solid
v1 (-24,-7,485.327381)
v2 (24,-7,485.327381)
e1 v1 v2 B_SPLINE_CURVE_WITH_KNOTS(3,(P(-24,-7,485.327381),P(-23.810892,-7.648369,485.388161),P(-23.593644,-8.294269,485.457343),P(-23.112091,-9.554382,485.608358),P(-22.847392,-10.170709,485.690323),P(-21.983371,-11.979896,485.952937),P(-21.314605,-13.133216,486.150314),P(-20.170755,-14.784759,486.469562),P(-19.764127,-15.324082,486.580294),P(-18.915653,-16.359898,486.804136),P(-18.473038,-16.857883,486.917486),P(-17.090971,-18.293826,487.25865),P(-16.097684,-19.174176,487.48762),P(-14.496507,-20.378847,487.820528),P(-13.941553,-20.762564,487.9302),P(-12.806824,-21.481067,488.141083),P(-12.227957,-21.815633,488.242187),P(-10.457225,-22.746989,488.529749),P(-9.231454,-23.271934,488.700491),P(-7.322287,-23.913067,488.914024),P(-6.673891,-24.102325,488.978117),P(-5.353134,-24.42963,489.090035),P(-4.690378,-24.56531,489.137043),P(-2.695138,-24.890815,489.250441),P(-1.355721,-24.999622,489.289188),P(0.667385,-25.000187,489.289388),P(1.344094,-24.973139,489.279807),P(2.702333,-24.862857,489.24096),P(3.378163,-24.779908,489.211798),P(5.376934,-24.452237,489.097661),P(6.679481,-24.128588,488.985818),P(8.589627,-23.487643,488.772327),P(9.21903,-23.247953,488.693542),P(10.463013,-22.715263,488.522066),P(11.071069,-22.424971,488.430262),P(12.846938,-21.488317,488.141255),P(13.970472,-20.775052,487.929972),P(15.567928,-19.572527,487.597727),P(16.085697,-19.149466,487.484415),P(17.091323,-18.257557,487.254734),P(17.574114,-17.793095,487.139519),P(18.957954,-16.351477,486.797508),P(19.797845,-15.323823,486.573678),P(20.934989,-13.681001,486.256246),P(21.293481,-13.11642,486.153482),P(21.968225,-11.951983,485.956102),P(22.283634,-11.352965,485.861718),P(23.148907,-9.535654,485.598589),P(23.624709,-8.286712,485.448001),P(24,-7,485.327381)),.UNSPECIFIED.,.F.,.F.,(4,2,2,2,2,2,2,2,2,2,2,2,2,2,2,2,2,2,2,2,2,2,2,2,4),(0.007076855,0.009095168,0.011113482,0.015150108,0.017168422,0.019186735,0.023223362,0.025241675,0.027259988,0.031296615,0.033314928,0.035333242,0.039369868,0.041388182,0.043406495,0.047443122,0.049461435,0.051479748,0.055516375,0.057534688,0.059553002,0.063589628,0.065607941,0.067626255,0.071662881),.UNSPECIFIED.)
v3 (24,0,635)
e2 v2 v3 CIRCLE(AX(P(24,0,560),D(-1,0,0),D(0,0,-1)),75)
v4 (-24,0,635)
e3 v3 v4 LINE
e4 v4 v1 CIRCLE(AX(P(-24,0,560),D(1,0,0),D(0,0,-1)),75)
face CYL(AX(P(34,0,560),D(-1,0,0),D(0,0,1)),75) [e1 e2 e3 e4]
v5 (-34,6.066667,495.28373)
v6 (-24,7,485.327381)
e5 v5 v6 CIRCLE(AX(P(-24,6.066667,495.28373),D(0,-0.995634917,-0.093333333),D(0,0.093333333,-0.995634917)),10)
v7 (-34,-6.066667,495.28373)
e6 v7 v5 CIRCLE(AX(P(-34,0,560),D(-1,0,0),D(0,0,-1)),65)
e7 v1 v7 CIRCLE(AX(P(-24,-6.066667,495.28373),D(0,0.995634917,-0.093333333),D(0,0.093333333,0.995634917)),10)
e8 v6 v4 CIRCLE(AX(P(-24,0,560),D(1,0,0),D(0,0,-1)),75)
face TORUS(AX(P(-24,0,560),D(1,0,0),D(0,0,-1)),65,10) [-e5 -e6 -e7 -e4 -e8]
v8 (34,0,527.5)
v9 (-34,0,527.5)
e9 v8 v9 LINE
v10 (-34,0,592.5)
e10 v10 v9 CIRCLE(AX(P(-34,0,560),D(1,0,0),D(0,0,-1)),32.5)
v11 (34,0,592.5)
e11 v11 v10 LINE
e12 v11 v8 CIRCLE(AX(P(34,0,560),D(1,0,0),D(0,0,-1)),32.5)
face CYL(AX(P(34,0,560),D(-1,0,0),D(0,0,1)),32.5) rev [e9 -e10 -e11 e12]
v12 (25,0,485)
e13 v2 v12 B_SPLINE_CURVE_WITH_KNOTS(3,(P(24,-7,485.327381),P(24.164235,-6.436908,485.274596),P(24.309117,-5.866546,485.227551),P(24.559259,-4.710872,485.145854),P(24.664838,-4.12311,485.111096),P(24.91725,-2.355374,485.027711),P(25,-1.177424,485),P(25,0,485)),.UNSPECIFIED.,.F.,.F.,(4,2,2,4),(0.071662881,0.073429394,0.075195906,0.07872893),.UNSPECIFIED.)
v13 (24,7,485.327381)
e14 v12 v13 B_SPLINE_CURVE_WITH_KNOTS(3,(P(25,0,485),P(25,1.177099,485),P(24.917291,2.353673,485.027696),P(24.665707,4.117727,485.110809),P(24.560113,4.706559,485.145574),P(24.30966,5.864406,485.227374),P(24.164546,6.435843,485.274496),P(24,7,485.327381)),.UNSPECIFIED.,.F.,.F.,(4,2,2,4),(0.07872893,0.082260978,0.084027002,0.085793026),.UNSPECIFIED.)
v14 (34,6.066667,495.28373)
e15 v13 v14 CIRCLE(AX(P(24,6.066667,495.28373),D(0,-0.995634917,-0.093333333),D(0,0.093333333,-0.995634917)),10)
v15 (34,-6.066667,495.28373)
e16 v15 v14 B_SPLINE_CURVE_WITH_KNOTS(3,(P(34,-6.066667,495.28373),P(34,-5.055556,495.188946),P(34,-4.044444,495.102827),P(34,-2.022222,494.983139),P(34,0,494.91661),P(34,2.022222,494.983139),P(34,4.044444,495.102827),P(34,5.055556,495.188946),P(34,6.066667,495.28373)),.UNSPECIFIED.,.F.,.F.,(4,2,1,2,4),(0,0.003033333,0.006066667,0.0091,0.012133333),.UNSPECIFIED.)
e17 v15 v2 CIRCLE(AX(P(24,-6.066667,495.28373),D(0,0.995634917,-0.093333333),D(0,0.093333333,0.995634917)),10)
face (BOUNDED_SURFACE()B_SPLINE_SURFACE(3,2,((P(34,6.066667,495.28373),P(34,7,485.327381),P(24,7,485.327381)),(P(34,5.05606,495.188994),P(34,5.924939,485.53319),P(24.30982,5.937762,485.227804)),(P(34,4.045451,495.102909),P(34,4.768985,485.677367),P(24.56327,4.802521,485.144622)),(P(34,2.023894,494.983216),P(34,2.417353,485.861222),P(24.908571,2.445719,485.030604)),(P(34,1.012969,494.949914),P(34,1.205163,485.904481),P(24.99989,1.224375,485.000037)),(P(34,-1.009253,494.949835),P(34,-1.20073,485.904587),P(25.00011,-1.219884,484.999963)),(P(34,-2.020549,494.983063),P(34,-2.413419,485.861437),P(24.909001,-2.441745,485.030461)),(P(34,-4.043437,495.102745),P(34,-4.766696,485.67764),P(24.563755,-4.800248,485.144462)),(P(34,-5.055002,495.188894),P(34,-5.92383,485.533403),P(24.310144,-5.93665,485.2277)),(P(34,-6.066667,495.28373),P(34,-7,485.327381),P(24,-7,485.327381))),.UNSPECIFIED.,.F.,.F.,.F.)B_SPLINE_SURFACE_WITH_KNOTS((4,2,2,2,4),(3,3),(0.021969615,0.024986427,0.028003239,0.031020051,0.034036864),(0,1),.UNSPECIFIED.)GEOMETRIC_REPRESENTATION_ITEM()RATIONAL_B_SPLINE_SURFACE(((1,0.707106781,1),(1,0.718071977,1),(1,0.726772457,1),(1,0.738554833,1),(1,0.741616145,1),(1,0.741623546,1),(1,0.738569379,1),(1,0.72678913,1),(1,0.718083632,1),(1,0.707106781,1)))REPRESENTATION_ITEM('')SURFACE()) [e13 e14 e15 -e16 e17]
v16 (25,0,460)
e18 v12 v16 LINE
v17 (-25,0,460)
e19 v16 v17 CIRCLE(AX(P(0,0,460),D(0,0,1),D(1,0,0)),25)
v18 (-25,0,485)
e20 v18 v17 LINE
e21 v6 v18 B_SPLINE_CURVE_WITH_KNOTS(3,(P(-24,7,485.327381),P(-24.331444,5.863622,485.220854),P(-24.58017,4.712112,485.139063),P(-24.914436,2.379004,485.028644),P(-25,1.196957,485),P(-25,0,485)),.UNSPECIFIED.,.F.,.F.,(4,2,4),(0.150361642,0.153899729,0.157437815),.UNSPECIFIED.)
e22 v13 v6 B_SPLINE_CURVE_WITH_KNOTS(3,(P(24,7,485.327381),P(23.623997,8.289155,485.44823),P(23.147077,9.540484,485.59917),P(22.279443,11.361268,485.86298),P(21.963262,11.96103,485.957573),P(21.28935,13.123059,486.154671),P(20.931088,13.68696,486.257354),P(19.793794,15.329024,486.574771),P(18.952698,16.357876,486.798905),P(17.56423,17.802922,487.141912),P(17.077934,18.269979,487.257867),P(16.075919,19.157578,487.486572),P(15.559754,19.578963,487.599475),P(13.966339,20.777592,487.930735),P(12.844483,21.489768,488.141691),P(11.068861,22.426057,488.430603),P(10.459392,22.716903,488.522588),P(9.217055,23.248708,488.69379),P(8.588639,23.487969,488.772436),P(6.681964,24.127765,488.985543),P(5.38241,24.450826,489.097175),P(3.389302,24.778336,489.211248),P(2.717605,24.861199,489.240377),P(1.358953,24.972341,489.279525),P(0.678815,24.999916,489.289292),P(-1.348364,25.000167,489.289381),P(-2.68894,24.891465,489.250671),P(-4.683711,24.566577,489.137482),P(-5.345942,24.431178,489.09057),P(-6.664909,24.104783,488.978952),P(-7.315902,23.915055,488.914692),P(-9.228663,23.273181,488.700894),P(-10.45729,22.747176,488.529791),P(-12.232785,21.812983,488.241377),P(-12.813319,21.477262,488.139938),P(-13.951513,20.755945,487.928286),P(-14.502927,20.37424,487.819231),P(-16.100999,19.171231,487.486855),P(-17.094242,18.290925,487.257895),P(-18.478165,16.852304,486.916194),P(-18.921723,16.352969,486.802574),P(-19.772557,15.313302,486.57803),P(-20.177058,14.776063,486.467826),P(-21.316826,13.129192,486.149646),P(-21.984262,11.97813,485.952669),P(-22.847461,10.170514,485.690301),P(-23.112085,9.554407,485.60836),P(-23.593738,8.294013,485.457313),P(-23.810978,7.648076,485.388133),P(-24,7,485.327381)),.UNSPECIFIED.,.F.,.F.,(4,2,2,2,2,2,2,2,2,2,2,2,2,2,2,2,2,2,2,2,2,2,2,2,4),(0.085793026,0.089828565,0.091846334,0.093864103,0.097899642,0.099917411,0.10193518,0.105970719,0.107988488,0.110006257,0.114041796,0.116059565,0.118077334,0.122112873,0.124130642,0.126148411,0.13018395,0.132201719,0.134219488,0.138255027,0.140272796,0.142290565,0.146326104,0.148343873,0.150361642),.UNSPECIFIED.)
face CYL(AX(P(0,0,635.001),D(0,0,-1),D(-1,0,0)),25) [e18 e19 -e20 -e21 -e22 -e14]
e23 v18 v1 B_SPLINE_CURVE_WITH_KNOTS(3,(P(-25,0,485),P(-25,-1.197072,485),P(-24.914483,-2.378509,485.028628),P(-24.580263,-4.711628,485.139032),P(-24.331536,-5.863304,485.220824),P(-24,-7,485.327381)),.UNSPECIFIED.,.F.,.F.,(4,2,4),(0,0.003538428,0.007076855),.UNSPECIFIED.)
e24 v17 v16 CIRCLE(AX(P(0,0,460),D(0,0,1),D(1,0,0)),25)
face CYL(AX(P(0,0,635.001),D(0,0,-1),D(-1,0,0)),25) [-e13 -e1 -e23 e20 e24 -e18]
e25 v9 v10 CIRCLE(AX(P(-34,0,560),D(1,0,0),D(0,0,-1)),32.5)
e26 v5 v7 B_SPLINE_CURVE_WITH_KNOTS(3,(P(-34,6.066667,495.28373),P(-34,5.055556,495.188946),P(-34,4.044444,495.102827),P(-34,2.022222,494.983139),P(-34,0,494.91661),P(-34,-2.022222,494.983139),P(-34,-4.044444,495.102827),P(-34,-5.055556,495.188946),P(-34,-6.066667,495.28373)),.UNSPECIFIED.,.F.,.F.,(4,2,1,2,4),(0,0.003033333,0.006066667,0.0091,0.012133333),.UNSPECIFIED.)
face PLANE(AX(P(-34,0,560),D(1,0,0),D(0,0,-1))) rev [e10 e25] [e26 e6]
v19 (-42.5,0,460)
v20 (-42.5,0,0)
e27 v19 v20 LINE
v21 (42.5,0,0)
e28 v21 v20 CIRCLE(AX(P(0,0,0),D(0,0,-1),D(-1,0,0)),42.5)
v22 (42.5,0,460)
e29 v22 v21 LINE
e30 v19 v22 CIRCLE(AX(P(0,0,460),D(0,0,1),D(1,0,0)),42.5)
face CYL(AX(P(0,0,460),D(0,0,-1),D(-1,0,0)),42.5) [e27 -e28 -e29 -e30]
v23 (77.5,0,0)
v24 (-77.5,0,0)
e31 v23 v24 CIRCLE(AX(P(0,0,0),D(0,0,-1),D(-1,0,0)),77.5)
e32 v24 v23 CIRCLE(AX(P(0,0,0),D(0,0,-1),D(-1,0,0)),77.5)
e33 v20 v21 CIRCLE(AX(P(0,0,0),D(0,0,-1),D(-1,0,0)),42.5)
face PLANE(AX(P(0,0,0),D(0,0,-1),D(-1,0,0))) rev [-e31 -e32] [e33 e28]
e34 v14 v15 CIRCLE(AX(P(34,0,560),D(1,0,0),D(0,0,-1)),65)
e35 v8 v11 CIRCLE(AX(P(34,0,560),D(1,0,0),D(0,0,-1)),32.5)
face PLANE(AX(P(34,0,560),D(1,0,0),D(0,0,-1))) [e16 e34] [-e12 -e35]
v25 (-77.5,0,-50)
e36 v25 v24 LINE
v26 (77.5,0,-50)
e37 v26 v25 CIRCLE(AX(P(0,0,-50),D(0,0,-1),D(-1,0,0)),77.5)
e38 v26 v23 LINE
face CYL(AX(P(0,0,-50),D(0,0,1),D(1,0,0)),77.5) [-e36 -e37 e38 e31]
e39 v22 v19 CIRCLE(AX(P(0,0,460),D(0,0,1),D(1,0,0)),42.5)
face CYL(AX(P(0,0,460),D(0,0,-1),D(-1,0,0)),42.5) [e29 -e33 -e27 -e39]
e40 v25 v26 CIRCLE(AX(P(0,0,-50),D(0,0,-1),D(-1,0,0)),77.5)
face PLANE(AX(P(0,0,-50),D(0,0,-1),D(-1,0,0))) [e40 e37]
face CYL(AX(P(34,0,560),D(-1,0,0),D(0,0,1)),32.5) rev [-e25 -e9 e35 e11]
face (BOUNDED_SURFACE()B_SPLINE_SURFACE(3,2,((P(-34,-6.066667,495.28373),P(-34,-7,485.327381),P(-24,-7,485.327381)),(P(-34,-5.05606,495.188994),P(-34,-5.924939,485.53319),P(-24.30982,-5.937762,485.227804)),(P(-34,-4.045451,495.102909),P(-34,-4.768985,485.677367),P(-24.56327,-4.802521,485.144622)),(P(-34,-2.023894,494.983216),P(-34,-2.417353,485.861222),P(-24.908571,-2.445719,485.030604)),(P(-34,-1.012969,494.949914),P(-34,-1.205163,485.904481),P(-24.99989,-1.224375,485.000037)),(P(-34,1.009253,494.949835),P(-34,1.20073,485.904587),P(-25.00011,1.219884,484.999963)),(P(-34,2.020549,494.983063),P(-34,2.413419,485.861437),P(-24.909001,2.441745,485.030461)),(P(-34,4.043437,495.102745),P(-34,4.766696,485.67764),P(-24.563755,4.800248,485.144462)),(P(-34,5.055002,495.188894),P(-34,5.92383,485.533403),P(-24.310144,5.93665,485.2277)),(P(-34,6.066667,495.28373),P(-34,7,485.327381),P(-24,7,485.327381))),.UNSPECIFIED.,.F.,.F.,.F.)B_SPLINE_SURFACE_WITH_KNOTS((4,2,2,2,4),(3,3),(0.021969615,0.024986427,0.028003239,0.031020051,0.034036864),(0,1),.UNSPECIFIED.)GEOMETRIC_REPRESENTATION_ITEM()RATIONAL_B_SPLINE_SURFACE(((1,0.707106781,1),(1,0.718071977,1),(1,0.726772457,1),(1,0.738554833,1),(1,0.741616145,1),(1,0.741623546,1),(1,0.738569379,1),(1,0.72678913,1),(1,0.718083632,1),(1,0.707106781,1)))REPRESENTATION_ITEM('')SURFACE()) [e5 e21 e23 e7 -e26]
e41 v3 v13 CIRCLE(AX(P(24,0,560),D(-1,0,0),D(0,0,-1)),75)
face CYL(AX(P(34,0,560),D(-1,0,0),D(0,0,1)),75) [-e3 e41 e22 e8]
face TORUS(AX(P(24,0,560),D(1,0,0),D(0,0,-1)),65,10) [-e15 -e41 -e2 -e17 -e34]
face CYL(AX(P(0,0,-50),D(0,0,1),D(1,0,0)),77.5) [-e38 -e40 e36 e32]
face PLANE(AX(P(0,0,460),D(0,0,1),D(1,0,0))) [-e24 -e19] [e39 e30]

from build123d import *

# Parameters (mm, degrees)
SKETCH_1_R           = 42.5
EXTRUDE_1_DEPTH      = 460
SKETCH_2_R           = 77.5
EXTRUDE_2_DEPTH      = 50
SKETCH_3_R           = 75.00000000000003
SKETCH_3_R_2         = 32.499999999999964
EXTRUDE_3_DEPTH      = 34
EXTRUDE_4_REACH      = 523.644
EXTRUDE_4_END_RADIUS = 75.00000000000003
SKETCH_4_R           = 25
FILLET_1_R           = 10


with BuildPart() as part:
    # 草图1 → 凸台-拉伸1 (new body)
    with BuildSketch(Plane.XY):
        Circle(SKETCH_1_R)
    extrude(amount=EXTRUDE_1_DEPTH)

    # 草图2 → 凸台-拉伸2 (add)
    with BuildSketch(Plane(origin=(0, 0, 0), x_dir=(-1, 0, 0), z_dir=(0, 0, -1))):
        Circle(SKETCH_2_R)
    extrude(amount=EXTRUDE_2_DEPTH)



with BuildPart() as body_2:
    # 草图3 → 凸台-拉伸3 (new, symmetric)
    with BuildSketch(Plane(origin=(0, 0, 0), x_dir=(0, 0, -1), z_dir=(1, 0, 0))):
        with Locations((-560, 0)):
            Circle(SKETCH_3_R)
        with Locations((-560, 0)):
            Circle(SKETCH_3_R_2, mode=Mode.SUBTRACT)
    extrude(amount=EXTRUDE_3_DEPTH, both=True)


with BuildPart() as part_1:
    add(part.part)

    add(body_2.part)  # 凸台-拉伸4 merges body 2
    # 凸台-拉伸4: up to this cylinder (the profile starts outside it)
    extrude_4_end = Plane(origin=(0, 0, 560), z_dir=(-1, 0, 0)) * Cylinder(EXTRUDE_4_END_RADIUS, 1198.288, mode=Mode.PRIVATE)
    # 草图4 → 凸台-拉伸4 (add, up to the surface)
    with BuildSketch(Plane.XY.offset(460), mode=Mode.PRIVATE) as extrude_4_sk1:
        with Locations(Location((0, 0, 0), (0, 0, 180))):
            Circle(SKETCH_4_R)
    extrude_4_tool1 = extrude(extrude_4_sk1.sketch, amount=EXTRUDE_4_REACH, mode=Mode.PRIVATE) - extrude_4_end
    add(extrude_4_tool1.solids().sort_by_distance((0, 0, 460))[0])

    # 圆角1
    fillet_1_edges = [part_1.edges().sort_by_distance(p)[0] for p in [
        (-34, 9.18e-15, 635),
        (34, 9.18e-15, 635),
    ]]
    fillet(fillet_1_edges, radius=FILLET_1_R)


solid = part_1.part
